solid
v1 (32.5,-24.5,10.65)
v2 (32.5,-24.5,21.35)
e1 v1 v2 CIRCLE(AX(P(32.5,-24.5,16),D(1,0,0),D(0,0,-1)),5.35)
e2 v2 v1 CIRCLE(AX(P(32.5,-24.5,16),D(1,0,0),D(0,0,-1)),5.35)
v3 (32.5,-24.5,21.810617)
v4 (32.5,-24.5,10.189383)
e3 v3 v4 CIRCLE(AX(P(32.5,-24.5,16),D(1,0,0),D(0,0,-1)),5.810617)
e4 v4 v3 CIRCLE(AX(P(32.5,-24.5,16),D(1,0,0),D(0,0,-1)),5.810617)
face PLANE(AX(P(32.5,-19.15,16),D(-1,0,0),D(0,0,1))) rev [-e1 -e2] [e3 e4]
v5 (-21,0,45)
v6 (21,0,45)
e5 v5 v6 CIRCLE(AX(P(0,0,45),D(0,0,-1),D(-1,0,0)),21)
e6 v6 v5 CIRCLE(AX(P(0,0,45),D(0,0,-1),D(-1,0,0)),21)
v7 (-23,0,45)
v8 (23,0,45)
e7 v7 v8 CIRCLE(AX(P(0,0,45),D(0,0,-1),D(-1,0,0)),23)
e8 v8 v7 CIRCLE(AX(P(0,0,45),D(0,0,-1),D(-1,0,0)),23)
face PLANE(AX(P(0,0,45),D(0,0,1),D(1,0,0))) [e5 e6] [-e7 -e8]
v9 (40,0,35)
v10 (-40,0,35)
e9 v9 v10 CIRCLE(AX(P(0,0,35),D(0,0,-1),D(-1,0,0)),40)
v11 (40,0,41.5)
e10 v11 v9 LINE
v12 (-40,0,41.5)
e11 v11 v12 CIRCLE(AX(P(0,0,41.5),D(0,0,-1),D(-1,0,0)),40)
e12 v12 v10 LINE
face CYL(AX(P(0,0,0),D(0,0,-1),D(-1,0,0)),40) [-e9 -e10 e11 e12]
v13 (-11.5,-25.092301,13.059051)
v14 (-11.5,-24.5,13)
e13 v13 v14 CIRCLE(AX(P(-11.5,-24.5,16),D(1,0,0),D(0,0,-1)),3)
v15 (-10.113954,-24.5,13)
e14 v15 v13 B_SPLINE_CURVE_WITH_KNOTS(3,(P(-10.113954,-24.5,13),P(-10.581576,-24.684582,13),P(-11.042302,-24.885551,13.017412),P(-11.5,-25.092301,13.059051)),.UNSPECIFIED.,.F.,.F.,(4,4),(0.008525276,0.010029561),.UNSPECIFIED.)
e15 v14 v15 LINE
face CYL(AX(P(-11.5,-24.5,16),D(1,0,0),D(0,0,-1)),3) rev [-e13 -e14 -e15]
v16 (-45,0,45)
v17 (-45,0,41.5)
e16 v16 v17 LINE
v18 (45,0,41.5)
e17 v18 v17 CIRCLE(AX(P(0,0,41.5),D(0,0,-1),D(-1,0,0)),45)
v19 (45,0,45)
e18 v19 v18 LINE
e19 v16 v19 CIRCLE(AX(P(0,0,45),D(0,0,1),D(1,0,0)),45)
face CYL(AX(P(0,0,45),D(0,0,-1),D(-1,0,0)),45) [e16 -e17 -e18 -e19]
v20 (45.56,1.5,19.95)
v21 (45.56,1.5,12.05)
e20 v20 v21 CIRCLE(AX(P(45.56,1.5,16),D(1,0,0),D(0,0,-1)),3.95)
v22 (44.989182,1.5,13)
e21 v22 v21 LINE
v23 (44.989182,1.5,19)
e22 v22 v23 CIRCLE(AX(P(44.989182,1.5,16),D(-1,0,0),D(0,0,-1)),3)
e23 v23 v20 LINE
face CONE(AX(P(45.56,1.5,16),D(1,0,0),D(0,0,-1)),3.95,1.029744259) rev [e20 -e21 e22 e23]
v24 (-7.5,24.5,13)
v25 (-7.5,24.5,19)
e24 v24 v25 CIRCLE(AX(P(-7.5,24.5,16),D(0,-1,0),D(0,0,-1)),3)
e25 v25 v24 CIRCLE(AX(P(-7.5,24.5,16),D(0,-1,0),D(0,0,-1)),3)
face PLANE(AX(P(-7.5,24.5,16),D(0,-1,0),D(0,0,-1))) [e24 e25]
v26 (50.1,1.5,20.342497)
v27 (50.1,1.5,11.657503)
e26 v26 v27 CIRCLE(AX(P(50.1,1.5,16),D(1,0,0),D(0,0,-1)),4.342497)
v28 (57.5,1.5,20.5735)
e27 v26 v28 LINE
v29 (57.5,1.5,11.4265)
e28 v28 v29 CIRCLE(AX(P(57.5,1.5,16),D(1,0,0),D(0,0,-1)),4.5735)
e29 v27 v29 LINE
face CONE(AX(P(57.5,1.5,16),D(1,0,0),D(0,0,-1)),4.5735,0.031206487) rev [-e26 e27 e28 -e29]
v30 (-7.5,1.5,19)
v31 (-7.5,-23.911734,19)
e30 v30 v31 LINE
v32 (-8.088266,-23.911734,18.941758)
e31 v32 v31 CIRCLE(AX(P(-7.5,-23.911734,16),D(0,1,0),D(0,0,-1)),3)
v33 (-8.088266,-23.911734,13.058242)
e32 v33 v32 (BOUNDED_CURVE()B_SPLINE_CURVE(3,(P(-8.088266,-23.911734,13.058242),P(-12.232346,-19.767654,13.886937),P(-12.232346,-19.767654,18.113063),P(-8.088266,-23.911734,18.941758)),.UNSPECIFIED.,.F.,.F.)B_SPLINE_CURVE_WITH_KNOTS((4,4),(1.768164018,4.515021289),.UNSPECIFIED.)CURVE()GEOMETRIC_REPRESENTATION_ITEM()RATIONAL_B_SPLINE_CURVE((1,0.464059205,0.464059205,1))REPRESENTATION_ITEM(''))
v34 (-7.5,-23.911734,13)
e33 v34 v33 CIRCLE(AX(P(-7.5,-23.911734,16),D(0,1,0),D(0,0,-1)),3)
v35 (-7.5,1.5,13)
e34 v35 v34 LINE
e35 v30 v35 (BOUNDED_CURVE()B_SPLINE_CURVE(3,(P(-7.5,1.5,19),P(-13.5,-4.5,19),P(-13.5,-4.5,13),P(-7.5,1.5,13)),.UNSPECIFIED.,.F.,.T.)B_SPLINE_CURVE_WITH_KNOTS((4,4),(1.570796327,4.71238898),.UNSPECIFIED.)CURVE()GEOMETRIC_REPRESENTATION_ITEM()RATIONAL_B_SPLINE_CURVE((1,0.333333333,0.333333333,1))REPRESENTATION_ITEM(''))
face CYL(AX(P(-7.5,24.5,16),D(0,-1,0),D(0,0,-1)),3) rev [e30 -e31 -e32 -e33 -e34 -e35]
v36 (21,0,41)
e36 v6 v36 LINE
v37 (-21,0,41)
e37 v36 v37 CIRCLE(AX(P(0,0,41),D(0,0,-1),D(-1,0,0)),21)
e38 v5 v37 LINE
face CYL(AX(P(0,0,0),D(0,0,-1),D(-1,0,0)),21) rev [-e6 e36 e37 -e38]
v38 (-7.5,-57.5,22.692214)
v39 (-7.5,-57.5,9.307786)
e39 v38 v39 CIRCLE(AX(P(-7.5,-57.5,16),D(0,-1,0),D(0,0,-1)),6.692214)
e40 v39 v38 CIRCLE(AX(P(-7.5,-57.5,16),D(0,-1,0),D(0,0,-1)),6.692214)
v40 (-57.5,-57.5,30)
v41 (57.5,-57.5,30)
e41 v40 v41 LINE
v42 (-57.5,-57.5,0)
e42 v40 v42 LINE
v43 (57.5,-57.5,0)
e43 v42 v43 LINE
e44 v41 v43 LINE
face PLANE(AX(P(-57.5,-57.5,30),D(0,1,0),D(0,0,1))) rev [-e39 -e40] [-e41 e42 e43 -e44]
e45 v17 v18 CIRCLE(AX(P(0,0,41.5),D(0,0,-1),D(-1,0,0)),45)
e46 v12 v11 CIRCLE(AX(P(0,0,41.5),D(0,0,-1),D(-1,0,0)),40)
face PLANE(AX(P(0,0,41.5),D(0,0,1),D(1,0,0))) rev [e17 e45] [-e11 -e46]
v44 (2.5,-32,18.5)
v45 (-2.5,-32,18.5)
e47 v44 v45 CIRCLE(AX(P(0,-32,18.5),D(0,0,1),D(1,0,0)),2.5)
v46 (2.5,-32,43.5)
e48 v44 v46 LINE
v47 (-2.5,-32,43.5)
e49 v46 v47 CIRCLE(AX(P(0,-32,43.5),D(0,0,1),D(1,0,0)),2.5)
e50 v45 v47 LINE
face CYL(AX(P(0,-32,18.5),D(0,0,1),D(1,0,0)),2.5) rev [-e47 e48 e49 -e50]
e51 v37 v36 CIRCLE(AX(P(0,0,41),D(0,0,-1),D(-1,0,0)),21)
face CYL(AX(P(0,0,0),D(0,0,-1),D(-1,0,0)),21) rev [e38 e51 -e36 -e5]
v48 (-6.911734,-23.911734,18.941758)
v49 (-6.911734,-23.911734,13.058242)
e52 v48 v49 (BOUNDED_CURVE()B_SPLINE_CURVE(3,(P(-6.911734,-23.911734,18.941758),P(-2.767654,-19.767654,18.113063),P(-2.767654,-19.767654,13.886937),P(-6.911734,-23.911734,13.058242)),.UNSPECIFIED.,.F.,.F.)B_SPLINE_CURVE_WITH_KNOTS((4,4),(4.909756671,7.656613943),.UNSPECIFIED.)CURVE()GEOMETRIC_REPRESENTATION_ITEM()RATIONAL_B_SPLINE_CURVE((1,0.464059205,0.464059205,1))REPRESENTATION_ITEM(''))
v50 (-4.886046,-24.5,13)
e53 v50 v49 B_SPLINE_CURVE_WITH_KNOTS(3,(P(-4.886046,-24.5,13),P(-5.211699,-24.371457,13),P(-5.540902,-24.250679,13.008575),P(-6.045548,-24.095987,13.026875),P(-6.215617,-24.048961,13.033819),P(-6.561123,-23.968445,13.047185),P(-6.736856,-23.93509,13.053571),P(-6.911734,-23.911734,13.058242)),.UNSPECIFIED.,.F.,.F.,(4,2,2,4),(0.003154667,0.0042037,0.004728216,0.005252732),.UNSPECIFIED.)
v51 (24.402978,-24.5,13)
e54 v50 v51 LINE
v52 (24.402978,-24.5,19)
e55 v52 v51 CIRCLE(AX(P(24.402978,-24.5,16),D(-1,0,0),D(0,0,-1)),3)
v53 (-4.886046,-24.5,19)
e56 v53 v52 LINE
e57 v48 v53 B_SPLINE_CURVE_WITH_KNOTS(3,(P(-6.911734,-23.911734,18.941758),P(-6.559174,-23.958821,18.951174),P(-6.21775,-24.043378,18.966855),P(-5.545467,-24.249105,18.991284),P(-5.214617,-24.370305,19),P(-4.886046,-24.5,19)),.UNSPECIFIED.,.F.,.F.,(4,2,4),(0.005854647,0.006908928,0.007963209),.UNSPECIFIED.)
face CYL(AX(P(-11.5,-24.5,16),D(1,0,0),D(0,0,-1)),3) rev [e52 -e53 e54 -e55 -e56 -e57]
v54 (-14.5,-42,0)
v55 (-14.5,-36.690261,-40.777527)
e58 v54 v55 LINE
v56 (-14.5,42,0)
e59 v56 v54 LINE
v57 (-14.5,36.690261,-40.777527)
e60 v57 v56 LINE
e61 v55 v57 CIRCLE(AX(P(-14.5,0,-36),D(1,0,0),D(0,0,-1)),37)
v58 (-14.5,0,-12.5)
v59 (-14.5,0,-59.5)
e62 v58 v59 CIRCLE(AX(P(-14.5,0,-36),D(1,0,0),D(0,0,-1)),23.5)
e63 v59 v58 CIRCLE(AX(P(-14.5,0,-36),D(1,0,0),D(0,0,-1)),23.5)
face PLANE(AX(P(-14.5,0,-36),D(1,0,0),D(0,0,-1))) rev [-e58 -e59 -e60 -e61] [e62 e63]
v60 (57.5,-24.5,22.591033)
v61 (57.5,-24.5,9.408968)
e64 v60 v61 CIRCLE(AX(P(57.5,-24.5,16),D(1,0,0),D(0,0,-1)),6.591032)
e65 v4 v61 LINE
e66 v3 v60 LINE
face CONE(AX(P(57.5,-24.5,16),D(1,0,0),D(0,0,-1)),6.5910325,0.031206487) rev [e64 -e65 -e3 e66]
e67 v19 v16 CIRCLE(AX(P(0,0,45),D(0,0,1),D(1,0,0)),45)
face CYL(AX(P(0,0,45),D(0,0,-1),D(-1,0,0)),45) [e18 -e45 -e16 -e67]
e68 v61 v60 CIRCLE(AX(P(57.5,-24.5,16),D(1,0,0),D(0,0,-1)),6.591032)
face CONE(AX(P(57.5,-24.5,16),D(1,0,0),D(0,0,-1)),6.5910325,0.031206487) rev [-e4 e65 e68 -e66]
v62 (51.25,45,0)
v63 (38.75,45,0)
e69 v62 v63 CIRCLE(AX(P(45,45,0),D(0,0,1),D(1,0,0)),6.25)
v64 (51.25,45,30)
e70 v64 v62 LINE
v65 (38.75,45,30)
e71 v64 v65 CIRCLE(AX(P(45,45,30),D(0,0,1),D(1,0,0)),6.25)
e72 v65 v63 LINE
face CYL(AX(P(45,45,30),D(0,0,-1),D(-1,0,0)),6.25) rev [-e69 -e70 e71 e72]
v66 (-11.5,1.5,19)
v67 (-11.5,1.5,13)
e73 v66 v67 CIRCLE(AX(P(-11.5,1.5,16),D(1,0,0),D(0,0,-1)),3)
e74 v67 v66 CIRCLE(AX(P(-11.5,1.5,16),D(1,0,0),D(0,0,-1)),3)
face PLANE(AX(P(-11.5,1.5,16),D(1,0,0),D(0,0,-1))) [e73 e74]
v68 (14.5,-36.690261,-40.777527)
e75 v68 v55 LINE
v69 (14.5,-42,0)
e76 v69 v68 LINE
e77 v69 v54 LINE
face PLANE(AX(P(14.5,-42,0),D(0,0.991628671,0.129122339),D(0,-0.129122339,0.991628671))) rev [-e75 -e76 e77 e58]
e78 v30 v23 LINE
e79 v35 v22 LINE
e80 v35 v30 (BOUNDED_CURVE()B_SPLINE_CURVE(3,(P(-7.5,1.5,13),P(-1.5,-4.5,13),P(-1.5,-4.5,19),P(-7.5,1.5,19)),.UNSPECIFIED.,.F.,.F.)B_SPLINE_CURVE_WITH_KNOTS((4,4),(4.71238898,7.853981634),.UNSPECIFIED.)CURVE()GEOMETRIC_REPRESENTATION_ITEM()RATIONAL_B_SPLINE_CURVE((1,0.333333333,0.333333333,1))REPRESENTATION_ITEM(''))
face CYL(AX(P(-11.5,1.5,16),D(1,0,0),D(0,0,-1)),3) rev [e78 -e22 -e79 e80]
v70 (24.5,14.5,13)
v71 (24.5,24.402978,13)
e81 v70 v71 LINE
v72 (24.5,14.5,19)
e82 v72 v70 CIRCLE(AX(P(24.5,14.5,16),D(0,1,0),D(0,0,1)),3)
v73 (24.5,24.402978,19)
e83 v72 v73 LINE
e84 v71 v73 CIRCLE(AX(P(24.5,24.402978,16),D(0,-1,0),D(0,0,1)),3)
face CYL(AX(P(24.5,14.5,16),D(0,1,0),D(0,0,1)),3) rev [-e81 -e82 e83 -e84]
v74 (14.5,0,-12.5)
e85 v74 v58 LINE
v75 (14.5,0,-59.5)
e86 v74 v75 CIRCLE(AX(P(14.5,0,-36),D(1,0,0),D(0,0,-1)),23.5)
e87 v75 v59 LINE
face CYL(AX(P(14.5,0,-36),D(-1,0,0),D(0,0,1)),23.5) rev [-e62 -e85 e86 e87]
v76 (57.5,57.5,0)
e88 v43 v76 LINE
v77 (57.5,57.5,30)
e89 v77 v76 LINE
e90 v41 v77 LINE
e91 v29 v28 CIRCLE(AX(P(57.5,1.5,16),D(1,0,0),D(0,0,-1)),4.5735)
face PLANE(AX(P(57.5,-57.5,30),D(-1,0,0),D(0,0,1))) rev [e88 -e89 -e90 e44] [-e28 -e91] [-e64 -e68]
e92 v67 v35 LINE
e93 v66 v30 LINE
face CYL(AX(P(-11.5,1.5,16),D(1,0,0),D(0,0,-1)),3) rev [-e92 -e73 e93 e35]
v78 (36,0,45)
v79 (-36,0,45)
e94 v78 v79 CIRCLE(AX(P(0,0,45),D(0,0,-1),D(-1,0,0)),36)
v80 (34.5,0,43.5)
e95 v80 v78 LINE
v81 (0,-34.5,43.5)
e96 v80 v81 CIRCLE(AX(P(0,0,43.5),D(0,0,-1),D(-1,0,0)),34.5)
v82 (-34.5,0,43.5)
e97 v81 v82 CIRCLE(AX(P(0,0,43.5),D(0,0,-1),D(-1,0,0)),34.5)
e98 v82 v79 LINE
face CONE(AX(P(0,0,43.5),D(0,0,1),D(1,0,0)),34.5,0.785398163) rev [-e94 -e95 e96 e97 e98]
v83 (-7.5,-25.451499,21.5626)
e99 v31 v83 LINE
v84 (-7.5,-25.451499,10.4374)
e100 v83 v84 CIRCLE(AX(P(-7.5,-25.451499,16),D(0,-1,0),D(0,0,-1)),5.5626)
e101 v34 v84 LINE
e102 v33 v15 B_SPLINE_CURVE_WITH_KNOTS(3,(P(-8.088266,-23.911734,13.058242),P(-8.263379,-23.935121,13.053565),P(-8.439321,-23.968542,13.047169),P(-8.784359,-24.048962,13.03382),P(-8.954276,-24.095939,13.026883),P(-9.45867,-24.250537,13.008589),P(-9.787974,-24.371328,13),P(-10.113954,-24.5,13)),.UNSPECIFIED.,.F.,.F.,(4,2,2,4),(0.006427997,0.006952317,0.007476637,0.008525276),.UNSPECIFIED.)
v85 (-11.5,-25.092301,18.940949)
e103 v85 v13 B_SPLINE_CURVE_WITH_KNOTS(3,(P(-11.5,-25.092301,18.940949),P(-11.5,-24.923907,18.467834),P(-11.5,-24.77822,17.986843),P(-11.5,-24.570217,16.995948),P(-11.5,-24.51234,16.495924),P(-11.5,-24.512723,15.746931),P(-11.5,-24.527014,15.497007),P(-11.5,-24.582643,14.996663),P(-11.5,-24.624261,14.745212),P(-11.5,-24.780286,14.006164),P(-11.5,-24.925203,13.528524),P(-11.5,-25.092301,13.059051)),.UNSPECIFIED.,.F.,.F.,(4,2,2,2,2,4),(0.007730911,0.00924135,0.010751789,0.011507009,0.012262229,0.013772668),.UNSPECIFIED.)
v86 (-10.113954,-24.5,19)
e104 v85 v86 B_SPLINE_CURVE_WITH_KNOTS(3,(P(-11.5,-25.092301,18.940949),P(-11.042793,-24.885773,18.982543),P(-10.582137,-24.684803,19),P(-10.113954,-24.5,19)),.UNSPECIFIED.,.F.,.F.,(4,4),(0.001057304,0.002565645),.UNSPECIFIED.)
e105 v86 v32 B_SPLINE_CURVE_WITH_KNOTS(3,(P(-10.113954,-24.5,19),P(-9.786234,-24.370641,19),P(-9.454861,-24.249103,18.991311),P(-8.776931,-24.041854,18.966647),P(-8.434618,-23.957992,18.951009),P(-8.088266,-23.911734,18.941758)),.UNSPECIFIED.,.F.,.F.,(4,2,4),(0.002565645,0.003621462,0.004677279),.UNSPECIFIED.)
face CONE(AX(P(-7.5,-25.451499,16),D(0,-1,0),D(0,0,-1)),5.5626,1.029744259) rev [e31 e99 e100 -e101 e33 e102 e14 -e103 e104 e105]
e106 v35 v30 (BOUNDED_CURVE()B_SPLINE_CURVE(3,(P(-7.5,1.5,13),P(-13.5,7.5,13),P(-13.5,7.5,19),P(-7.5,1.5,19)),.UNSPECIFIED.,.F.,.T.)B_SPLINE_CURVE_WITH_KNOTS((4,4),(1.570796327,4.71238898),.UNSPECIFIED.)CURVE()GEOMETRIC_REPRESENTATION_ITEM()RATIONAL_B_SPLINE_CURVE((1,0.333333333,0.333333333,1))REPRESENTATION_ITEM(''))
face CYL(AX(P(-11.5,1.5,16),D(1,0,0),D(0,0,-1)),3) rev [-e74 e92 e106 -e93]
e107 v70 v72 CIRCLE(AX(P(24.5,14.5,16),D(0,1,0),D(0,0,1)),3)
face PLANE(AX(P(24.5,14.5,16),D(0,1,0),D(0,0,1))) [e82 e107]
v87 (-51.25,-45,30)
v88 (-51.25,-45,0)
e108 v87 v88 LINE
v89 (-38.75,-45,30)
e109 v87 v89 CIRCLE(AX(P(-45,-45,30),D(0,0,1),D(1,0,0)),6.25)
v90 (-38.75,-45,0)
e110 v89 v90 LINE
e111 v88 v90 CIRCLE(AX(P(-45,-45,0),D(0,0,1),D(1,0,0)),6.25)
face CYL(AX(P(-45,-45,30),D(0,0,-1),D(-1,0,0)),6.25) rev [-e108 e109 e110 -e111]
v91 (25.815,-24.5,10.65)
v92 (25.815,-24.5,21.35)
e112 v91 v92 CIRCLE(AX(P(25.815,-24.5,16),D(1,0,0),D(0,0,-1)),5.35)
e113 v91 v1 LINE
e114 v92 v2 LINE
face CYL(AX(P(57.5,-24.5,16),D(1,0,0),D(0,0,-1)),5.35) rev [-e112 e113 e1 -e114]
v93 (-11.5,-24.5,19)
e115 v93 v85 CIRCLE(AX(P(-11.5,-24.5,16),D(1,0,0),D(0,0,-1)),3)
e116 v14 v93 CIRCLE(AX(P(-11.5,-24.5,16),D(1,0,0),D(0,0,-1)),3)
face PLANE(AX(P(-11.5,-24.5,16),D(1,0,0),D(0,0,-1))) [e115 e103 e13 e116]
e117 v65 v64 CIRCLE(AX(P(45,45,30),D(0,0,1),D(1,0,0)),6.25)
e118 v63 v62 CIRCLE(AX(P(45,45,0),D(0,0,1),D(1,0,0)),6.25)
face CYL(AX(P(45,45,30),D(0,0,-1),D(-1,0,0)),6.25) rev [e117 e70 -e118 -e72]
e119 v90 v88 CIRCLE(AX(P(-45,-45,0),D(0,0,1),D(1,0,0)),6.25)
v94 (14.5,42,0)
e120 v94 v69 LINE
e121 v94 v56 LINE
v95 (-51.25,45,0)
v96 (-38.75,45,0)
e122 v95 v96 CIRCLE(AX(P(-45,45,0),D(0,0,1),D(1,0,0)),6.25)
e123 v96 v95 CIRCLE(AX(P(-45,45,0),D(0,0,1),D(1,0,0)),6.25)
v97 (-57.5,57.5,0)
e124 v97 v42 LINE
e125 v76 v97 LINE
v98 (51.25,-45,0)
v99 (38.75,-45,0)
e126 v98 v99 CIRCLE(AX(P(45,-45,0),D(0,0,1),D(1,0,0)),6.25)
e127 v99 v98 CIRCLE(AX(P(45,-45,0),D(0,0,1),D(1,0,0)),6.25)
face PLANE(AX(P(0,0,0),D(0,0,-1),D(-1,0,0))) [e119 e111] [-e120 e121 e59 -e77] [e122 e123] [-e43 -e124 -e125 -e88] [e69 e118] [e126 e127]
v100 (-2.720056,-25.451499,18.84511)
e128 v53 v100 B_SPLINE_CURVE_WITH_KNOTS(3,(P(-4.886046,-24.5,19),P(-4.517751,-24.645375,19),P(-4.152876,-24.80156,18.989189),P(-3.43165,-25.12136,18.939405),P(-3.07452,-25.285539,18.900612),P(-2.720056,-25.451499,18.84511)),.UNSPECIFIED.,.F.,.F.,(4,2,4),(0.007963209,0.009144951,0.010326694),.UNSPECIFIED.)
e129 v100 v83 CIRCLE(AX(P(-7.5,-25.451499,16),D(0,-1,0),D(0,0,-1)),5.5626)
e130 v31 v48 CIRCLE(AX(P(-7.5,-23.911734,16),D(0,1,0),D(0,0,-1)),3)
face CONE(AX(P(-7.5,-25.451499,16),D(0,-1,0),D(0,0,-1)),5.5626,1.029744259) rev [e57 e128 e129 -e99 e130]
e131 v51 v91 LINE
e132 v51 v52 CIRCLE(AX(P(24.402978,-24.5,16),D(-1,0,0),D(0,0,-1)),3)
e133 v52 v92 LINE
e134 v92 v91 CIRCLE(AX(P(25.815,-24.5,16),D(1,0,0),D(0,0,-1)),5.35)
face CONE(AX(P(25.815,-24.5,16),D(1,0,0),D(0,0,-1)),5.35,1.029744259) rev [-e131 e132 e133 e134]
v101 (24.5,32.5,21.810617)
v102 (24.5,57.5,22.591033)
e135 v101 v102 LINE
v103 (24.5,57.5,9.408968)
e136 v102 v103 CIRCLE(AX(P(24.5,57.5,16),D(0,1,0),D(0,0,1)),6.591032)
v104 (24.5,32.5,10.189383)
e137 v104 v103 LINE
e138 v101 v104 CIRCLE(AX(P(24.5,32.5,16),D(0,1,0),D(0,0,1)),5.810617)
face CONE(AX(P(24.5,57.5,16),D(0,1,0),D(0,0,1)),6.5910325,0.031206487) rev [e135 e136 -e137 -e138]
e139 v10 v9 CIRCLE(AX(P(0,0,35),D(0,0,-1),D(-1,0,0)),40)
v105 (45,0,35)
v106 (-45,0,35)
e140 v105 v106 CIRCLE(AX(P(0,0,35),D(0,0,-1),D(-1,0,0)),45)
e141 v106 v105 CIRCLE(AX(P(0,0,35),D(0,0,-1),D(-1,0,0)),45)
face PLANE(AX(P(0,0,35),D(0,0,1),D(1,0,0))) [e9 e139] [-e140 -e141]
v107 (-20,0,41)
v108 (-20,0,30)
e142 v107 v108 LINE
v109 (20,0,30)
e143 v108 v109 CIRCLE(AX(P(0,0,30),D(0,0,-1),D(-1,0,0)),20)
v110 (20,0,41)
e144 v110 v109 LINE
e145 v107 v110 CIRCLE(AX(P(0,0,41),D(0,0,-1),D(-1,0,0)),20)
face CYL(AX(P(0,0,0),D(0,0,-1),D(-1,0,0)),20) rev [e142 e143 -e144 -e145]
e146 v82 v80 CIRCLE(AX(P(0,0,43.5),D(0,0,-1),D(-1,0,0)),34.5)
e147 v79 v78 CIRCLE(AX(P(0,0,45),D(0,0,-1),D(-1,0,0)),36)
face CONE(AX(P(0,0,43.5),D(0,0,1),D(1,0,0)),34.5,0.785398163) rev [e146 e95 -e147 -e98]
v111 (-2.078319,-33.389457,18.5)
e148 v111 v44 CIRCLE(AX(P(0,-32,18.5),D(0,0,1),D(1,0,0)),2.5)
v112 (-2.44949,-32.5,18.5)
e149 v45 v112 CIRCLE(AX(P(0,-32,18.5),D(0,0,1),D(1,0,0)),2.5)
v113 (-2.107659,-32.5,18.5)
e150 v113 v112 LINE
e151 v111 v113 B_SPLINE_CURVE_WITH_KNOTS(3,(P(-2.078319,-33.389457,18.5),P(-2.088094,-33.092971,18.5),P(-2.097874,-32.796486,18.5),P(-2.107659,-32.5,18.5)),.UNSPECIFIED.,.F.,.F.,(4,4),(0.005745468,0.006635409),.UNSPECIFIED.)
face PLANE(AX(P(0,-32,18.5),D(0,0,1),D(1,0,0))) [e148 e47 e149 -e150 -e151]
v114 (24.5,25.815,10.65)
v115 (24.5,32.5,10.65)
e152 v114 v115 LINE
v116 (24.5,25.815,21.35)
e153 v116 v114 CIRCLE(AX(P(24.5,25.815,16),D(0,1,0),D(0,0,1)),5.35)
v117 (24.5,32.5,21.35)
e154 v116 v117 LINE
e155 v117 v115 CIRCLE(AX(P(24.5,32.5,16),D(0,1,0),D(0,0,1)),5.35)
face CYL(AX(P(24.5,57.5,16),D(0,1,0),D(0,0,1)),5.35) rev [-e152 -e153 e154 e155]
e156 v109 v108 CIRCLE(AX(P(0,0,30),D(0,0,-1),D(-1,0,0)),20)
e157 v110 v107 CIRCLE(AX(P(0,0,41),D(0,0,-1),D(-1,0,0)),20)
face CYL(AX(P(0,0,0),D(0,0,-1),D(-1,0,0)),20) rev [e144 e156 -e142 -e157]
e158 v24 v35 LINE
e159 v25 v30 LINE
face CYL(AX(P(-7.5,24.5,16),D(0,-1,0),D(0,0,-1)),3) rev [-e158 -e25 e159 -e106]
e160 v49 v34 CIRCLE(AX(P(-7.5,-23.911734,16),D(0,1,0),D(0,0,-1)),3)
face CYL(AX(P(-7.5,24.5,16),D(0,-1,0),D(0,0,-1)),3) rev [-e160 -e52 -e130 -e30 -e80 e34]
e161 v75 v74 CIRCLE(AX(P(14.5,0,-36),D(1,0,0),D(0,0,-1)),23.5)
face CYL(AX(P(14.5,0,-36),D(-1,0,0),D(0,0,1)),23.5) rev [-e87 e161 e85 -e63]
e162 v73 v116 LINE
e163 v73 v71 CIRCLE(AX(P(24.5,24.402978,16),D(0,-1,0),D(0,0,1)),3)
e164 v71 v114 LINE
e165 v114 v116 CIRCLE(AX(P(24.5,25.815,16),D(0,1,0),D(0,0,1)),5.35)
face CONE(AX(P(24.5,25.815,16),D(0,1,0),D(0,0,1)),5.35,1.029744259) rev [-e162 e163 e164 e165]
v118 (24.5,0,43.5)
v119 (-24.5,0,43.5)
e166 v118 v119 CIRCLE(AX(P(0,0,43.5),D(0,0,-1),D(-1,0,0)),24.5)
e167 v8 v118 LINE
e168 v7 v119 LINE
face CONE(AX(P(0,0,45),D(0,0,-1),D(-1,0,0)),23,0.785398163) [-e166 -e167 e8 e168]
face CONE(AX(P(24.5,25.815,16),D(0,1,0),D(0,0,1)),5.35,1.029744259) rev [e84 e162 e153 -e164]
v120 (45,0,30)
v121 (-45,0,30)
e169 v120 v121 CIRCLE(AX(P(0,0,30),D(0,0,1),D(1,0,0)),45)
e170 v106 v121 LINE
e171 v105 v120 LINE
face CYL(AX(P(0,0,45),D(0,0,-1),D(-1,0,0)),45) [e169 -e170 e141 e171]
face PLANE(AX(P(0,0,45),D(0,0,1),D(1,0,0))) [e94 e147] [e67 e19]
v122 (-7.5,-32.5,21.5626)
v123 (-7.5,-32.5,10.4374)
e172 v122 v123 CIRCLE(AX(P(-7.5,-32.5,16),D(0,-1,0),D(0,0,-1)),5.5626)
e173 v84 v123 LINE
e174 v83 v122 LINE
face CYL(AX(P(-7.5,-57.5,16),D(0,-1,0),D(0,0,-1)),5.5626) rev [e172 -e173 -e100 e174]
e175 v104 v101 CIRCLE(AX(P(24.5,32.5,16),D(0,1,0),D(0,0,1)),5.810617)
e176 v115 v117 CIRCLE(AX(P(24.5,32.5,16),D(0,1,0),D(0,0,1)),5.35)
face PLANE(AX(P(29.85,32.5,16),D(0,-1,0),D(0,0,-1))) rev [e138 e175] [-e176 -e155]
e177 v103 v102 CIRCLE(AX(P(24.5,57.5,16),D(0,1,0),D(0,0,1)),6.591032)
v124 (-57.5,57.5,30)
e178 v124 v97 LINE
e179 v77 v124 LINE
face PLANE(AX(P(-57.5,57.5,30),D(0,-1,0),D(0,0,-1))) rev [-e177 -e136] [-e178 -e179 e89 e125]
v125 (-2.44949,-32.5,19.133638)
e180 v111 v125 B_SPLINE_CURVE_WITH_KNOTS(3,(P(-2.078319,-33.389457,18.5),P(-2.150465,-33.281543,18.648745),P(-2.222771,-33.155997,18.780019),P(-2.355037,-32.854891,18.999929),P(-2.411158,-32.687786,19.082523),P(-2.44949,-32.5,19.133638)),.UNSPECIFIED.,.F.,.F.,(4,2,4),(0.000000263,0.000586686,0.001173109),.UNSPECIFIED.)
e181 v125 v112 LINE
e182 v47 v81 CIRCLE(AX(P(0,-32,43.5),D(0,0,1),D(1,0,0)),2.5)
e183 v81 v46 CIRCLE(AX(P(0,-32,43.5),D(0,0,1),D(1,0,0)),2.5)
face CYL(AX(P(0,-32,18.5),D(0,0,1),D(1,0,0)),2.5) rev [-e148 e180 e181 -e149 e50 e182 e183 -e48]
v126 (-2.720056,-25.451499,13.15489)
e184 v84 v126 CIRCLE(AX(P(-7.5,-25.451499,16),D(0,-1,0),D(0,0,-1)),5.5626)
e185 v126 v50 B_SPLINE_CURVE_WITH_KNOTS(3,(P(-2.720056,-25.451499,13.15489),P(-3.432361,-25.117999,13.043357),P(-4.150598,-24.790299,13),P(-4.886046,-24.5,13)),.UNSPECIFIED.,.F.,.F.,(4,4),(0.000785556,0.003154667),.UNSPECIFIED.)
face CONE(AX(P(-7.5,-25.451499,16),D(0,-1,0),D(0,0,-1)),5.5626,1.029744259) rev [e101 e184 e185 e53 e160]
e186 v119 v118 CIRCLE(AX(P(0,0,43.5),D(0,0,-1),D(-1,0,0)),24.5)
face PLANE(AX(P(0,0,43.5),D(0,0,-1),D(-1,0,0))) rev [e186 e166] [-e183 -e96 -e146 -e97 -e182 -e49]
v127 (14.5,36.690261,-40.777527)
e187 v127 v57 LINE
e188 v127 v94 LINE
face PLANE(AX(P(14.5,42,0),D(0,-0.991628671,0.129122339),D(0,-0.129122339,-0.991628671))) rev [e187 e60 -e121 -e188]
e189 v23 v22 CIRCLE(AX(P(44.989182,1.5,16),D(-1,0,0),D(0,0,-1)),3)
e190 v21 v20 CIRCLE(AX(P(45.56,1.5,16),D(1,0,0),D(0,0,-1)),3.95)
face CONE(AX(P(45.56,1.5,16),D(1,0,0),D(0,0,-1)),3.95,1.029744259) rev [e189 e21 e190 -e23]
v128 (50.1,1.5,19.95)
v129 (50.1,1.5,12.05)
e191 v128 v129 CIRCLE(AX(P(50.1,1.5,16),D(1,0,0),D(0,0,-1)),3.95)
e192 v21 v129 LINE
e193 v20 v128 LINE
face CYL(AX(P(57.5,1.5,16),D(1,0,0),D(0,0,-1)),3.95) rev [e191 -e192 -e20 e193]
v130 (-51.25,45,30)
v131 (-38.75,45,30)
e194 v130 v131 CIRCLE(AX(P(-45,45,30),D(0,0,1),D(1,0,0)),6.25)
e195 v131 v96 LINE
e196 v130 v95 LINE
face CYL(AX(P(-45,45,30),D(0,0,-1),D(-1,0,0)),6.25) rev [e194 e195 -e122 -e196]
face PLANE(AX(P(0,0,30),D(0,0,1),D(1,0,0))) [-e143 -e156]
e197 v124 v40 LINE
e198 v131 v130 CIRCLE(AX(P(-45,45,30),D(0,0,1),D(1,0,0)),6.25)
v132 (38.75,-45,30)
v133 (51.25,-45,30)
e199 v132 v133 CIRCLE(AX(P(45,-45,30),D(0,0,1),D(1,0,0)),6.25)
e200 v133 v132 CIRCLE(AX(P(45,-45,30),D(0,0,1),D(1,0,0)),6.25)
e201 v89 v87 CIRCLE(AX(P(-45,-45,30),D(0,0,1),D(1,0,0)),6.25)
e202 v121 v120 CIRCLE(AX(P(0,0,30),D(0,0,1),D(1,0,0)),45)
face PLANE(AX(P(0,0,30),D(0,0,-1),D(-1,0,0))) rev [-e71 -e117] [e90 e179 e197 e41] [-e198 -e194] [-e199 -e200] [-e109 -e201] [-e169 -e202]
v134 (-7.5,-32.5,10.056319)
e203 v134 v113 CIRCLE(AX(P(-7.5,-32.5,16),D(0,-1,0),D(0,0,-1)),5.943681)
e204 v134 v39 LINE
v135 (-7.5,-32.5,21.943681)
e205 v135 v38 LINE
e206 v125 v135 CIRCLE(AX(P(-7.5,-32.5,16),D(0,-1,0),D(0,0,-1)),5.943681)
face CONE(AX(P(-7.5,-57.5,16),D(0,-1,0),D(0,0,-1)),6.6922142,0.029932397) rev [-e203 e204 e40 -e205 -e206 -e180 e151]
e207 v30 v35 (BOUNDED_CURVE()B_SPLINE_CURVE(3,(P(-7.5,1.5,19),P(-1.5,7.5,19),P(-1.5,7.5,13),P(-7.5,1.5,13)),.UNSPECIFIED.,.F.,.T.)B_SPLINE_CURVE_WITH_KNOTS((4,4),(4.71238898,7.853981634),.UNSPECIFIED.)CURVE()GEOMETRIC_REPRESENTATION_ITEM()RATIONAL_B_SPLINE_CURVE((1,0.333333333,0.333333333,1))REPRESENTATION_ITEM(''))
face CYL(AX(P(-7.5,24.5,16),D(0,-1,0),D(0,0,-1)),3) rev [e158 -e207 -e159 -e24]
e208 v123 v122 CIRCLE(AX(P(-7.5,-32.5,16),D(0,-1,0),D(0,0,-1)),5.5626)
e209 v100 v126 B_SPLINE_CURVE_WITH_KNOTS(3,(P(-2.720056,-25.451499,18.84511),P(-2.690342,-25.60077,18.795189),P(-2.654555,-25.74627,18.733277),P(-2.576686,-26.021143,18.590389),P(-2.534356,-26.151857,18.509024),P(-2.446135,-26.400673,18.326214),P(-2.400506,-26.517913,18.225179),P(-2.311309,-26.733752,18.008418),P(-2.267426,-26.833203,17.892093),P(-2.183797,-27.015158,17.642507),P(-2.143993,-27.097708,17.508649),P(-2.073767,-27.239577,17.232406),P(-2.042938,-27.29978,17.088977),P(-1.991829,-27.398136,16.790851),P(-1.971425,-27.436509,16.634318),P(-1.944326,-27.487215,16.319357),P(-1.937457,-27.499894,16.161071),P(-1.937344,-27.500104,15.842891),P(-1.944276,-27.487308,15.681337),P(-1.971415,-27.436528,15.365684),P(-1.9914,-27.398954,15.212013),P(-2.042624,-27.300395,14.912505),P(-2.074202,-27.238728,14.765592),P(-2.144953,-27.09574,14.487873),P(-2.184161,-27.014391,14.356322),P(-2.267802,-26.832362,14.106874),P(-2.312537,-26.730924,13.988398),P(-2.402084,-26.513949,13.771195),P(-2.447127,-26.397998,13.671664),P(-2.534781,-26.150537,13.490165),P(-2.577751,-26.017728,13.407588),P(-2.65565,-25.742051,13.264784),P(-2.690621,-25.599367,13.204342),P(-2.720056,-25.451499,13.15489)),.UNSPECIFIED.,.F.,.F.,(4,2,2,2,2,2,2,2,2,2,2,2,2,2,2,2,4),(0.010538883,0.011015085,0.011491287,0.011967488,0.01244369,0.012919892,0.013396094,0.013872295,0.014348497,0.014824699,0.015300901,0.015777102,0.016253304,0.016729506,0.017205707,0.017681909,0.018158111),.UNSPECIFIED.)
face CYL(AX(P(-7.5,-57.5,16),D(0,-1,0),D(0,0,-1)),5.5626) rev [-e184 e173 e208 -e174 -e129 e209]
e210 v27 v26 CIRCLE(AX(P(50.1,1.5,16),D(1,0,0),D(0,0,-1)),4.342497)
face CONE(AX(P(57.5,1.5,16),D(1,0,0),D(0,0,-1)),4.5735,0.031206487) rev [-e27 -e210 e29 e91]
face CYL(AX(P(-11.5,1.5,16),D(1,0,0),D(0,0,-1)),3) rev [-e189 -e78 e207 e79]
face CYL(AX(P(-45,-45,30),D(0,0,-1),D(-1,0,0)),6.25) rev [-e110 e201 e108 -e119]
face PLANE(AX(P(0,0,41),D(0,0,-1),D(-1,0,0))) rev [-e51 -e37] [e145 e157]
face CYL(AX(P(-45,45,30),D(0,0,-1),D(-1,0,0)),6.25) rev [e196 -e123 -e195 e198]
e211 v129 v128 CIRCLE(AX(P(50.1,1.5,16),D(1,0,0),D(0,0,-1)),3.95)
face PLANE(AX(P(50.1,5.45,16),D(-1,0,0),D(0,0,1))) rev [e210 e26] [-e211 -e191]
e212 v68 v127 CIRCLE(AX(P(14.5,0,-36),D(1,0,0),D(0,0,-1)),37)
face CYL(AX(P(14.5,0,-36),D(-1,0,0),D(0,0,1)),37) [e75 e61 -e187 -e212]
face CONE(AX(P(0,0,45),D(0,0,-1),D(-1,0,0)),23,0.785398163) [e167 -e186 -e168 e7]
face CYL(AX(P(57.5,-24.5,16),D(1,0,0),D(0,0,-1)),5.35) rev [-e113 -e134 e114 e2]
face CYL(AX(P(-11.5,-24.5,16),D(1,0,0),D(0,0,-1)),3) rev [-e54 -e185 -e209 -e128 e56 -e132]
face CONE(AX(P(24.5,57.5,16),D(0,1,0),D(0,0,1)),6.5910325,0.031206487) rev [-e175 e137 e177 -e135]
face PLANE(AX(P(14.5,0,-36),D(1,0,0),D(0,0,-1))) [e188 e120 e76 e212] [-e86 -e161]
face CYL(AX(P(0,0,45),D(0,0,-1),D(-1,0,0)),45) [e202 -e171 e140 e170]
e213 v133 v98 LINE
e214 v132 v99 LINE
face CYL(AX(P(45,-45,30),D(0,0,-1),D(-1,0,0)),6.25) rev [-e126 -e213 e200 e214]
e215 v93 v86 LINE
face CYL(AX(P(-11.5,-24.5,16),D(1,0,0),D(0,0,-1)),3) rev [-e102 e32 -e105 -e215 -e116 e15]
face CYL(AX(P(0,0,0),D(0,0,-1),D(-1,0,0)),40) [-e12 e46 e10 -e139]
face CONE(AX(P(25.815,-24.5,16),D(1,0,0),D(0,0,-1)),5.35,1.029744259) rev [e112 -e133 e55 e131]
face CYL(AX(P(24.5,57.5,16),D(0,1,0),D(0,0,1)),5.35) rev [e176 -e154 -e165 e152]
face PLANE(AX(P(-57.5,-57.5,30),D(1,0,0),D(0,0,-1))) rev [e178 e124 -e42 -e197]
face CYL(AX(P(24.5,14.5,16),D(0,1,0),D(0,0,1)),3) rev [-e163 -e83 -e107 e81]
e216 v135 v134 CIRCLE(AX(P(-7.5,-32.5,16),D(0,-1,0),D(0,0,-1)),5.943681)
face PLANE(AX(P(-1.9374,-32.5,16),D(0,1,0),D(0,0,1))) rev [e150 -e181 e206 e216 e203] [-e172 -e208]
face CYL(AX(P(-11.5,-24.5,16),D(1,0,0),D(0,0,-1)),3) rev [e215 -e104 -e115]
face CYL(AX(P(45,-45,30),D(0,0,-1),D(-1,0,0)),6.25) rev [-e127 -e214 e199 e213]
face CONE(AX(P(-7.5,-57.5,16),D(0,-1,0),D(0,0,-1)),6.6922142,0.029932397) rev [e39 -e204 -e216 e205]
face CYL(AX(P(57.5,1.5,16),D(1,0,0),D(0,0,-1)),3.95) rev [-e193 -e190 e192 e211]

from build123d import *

# Parameters (mm, degrees)
SKETCH_1_W          = 115
SKETCH_1_H          = 115
SKETCH_1_R          = 6.25
EXTRUDE_1_DEPTH     = 30
SKETCH_2_R          = 45
EXTRUDE_2_DEPTH     = 15
SKETCH_3_W          = 6.5
SKETCH_3_H          = 5
SKETCH_4_R          = 2.5
CUT_EXTRUDE_1_DEPTH = 25
SKETCH_17_R         = 3
CUT_EXTRUDE_2_DEPTH = 43
SKETCH_18_R         = 3
CUT_EXTRUDE_3_DEPTH = 69
SKETCH_19_R         = 3
CUT_EXTRUDE_4_DEPTH = 82
SKETCH_20_R         = 23.5
EXTRUDE_3_DEPTH     = 14.5


with BuildPart() as part:
    # 草图1 → 凸台-拉伸1 (new body)
    with BuildSketch(Plane.XY):
        Rectangle(SKETCH_1_W, SKETCH_1_H)
        with Locations((-45, 45)):
            Circle(SKETCH_1_R, mode=Mode.SUBTRACT)
        with Locations((45, 45)):
            Circle(SKETCH_1_R, mode=Mode.SUBTRACT)
        with Locations((45, -45)):
            Circle(SKETCH_1_R, mode=Mode.SUBTRACT)
        with Locations((-45, -45)):
            Circle(SKETCH_1_R, mode=Mode.SUBTRACT)
    extrude(amount=EXTRUDE_1_DEPTH)

    # 草图2 → 凸台-拉伸2 (add)
    with BuildSketch(Plane.XY.offset(30)):
        Circle(SKETCH_2_R)
    extrude(amount=EXTRUDE_2_DEPTH)

    # 草图3 → 切除-旋转1 (revolve, cut)
    with BuildSketch(Plane(origin=(0, 0, 0), x_dir=(0, 0, -1), z_dir=(1, 0, 0)), mode=Mode.PRIVATE) as cut_revolve_1_sk:
        Polygon((-43.5, 34.5), (-45, 36), (-45, 23), (-43.5, 24.5), align=None)
        Polygon((-30, 0), (-45, 0), (-45, 21), (-41, 21), (-41, 20), (-30, 20), align=None)
        with Locations((-38.25, 42.5)):
            Rectangle(SKETCH_3_W, SKETCH_3_H)
    revolve(cut_revolve_1_sk.sketch.rotate(Axis((0, 0, 0), (0, 0, 1)), 90), axis=Axis((0, 0, 0), (0, 0, 1)), mode=Mode.SUBTRACT)

    # 草图4 → 切除-拉伸1 (cut)
    with BuildSketch(Plane.XY.offset(43.5)):
        with Locations((0, -32)):
            Circle(SKETCH_4_R)
    extrude(amount=-CUT_EXTRUDE_1_DEPTH, mode=Mode.SUBTRACT)

    # 草图6 → 1/4 NPT 螺纹孔1 (revolve, cut)
    with BuildSketch(Plane(origin=(-7.5, -57.5, 16), x_dir=(0, 0, -1), z_dir=(1, 0, 0))):
        Polygon((0, 0), (0, 35.390848279), (5.5626, 32.048501), (5.5626, 25), (5.943680721, 25), (6.6922142, 0), align=None)
    revolve(axis=Axis((-7.5, -63.85, 16), (0, 1, 0)), mode=Mode.SUBTRACT)

    # 草图9 → 1/4 Rc 螺纹孔1 (revolve, cut)
    with BuildSketch(Plane(origin=(57.5, -24.5, 16), x_dir=(0, 0, -1), z_dir=(0, 1, 0))):
        Polygon((0, 0), (0, 34.899604312), (5.35, 31.685), (5.35, 25), (5.810616973, 25), (6.5910325, 0), align=None)
    revolve(axis=Axis((63.85, -24.5, 16), (-1, 0, 0)), mode=Mode.SUBTRACT)

    # 草图12 → 1/8 Rc 螺纹孔1 (revolve, cut)
    with BuildSketch(Plane(origin=(57.5, 1.5, 16), x_dir=(0, 0, -1), z_dir=(0, 1, 0))):
        Polygon((0, 0), (0, 14.313399445), (3.95, 11.94), (3.95, 7.4), (4.342497004, 7.4), (4.5735, 0), align=None)
    revolve(axis=Axis((63.85, 1.5, 16), (-1, 0, 0)), mode=Mode.SUBTRACT)

    # 草图15 → 1/4 Rc 螺纹孔2 (revolve, cut)
    with BuildSketch(Plane(origin=(24.5, 57.5, 16), x_dir=(0, 0, 1), z_dir=(1, 0, 0))):
        Polygon((0, 0), (0, 34.899604312), (5.35, 31.685), (5.35, 25), (5.810616973, 25), (6.5910325, 0), align=None)
    revolve(axis=Axis((24.5, 63.85, 16), (0, -1, 0)), mode=Mode.SUBTRACT)

    # 草图17 → 切除-拉伸2 (cut)
    with BuildSketch(Plane(origin=(0, 57.5, 0), x_dir=(1, 0, 0), z_dir=(0, 1, 0))):
        with Locations(Location((24.5, -16, 0), (0, 0, 270))):
            Circle(SKETCH_17_R)
    extrude(amount=-CUT_EXTRUDE_2_DEPTH, mode=Mode.SUBTRACT)

    # 草图18 → 切除-拉伸3 (cut)
    with BuildSketch(Plane(origin=(57.5, 0, 0), x_dir=(0, 0, -1), z_dir=(1, 0, 0))):
        with Locations((-16, 1.5)):
            Circle(SKETCH_18_R)
        with Locations((-16, -24.5)):
            Circle(SKETCH_18_R)
    extrude(amount=-CUT_EXTRUDE_3_DEPTH, mode=Mode.SUBTRACT)

    # 草图19 → 切除-拉伸4 (cut)
    with BuildSketch(Plane.XZ.offset(57.5)):
        with Locations(Location((-7.5, 16, 0), (0, 0, 270))):
            Circle(SKETCH_19_R)
    extrude(amount=-CUT_EXTRUDE_4_DEPTH, mode=Mode.SUBTRACT)

    # 草图20 → 凸台-拉伸3 (add, symmetric)
    with BuildSketch(Plane(origin=(0, 0, 0), x_dir=(0, 0, -1), z_dir=(1, 0, 0))):
        with BuildLine():
            Line((0, 42), (0, -42))
            Line((0, -42), (40.777526531, -36.690260836))
            ThreePointArc((40.777526531, -36.690260836), (73, 0), (40.777526531, 36.690260836))
            Line((40.777526531, 36.690260836), (0, 42))
        make_face()
        with Locations(Location((36, 0, 0), (0, 0, 180))):
            Circle(SKETCH_20_R, mode=Mode.SUBTRACT)
    extrude(amount=EXTRUDE_3_DEPTH, both=True)


solid = part.part
